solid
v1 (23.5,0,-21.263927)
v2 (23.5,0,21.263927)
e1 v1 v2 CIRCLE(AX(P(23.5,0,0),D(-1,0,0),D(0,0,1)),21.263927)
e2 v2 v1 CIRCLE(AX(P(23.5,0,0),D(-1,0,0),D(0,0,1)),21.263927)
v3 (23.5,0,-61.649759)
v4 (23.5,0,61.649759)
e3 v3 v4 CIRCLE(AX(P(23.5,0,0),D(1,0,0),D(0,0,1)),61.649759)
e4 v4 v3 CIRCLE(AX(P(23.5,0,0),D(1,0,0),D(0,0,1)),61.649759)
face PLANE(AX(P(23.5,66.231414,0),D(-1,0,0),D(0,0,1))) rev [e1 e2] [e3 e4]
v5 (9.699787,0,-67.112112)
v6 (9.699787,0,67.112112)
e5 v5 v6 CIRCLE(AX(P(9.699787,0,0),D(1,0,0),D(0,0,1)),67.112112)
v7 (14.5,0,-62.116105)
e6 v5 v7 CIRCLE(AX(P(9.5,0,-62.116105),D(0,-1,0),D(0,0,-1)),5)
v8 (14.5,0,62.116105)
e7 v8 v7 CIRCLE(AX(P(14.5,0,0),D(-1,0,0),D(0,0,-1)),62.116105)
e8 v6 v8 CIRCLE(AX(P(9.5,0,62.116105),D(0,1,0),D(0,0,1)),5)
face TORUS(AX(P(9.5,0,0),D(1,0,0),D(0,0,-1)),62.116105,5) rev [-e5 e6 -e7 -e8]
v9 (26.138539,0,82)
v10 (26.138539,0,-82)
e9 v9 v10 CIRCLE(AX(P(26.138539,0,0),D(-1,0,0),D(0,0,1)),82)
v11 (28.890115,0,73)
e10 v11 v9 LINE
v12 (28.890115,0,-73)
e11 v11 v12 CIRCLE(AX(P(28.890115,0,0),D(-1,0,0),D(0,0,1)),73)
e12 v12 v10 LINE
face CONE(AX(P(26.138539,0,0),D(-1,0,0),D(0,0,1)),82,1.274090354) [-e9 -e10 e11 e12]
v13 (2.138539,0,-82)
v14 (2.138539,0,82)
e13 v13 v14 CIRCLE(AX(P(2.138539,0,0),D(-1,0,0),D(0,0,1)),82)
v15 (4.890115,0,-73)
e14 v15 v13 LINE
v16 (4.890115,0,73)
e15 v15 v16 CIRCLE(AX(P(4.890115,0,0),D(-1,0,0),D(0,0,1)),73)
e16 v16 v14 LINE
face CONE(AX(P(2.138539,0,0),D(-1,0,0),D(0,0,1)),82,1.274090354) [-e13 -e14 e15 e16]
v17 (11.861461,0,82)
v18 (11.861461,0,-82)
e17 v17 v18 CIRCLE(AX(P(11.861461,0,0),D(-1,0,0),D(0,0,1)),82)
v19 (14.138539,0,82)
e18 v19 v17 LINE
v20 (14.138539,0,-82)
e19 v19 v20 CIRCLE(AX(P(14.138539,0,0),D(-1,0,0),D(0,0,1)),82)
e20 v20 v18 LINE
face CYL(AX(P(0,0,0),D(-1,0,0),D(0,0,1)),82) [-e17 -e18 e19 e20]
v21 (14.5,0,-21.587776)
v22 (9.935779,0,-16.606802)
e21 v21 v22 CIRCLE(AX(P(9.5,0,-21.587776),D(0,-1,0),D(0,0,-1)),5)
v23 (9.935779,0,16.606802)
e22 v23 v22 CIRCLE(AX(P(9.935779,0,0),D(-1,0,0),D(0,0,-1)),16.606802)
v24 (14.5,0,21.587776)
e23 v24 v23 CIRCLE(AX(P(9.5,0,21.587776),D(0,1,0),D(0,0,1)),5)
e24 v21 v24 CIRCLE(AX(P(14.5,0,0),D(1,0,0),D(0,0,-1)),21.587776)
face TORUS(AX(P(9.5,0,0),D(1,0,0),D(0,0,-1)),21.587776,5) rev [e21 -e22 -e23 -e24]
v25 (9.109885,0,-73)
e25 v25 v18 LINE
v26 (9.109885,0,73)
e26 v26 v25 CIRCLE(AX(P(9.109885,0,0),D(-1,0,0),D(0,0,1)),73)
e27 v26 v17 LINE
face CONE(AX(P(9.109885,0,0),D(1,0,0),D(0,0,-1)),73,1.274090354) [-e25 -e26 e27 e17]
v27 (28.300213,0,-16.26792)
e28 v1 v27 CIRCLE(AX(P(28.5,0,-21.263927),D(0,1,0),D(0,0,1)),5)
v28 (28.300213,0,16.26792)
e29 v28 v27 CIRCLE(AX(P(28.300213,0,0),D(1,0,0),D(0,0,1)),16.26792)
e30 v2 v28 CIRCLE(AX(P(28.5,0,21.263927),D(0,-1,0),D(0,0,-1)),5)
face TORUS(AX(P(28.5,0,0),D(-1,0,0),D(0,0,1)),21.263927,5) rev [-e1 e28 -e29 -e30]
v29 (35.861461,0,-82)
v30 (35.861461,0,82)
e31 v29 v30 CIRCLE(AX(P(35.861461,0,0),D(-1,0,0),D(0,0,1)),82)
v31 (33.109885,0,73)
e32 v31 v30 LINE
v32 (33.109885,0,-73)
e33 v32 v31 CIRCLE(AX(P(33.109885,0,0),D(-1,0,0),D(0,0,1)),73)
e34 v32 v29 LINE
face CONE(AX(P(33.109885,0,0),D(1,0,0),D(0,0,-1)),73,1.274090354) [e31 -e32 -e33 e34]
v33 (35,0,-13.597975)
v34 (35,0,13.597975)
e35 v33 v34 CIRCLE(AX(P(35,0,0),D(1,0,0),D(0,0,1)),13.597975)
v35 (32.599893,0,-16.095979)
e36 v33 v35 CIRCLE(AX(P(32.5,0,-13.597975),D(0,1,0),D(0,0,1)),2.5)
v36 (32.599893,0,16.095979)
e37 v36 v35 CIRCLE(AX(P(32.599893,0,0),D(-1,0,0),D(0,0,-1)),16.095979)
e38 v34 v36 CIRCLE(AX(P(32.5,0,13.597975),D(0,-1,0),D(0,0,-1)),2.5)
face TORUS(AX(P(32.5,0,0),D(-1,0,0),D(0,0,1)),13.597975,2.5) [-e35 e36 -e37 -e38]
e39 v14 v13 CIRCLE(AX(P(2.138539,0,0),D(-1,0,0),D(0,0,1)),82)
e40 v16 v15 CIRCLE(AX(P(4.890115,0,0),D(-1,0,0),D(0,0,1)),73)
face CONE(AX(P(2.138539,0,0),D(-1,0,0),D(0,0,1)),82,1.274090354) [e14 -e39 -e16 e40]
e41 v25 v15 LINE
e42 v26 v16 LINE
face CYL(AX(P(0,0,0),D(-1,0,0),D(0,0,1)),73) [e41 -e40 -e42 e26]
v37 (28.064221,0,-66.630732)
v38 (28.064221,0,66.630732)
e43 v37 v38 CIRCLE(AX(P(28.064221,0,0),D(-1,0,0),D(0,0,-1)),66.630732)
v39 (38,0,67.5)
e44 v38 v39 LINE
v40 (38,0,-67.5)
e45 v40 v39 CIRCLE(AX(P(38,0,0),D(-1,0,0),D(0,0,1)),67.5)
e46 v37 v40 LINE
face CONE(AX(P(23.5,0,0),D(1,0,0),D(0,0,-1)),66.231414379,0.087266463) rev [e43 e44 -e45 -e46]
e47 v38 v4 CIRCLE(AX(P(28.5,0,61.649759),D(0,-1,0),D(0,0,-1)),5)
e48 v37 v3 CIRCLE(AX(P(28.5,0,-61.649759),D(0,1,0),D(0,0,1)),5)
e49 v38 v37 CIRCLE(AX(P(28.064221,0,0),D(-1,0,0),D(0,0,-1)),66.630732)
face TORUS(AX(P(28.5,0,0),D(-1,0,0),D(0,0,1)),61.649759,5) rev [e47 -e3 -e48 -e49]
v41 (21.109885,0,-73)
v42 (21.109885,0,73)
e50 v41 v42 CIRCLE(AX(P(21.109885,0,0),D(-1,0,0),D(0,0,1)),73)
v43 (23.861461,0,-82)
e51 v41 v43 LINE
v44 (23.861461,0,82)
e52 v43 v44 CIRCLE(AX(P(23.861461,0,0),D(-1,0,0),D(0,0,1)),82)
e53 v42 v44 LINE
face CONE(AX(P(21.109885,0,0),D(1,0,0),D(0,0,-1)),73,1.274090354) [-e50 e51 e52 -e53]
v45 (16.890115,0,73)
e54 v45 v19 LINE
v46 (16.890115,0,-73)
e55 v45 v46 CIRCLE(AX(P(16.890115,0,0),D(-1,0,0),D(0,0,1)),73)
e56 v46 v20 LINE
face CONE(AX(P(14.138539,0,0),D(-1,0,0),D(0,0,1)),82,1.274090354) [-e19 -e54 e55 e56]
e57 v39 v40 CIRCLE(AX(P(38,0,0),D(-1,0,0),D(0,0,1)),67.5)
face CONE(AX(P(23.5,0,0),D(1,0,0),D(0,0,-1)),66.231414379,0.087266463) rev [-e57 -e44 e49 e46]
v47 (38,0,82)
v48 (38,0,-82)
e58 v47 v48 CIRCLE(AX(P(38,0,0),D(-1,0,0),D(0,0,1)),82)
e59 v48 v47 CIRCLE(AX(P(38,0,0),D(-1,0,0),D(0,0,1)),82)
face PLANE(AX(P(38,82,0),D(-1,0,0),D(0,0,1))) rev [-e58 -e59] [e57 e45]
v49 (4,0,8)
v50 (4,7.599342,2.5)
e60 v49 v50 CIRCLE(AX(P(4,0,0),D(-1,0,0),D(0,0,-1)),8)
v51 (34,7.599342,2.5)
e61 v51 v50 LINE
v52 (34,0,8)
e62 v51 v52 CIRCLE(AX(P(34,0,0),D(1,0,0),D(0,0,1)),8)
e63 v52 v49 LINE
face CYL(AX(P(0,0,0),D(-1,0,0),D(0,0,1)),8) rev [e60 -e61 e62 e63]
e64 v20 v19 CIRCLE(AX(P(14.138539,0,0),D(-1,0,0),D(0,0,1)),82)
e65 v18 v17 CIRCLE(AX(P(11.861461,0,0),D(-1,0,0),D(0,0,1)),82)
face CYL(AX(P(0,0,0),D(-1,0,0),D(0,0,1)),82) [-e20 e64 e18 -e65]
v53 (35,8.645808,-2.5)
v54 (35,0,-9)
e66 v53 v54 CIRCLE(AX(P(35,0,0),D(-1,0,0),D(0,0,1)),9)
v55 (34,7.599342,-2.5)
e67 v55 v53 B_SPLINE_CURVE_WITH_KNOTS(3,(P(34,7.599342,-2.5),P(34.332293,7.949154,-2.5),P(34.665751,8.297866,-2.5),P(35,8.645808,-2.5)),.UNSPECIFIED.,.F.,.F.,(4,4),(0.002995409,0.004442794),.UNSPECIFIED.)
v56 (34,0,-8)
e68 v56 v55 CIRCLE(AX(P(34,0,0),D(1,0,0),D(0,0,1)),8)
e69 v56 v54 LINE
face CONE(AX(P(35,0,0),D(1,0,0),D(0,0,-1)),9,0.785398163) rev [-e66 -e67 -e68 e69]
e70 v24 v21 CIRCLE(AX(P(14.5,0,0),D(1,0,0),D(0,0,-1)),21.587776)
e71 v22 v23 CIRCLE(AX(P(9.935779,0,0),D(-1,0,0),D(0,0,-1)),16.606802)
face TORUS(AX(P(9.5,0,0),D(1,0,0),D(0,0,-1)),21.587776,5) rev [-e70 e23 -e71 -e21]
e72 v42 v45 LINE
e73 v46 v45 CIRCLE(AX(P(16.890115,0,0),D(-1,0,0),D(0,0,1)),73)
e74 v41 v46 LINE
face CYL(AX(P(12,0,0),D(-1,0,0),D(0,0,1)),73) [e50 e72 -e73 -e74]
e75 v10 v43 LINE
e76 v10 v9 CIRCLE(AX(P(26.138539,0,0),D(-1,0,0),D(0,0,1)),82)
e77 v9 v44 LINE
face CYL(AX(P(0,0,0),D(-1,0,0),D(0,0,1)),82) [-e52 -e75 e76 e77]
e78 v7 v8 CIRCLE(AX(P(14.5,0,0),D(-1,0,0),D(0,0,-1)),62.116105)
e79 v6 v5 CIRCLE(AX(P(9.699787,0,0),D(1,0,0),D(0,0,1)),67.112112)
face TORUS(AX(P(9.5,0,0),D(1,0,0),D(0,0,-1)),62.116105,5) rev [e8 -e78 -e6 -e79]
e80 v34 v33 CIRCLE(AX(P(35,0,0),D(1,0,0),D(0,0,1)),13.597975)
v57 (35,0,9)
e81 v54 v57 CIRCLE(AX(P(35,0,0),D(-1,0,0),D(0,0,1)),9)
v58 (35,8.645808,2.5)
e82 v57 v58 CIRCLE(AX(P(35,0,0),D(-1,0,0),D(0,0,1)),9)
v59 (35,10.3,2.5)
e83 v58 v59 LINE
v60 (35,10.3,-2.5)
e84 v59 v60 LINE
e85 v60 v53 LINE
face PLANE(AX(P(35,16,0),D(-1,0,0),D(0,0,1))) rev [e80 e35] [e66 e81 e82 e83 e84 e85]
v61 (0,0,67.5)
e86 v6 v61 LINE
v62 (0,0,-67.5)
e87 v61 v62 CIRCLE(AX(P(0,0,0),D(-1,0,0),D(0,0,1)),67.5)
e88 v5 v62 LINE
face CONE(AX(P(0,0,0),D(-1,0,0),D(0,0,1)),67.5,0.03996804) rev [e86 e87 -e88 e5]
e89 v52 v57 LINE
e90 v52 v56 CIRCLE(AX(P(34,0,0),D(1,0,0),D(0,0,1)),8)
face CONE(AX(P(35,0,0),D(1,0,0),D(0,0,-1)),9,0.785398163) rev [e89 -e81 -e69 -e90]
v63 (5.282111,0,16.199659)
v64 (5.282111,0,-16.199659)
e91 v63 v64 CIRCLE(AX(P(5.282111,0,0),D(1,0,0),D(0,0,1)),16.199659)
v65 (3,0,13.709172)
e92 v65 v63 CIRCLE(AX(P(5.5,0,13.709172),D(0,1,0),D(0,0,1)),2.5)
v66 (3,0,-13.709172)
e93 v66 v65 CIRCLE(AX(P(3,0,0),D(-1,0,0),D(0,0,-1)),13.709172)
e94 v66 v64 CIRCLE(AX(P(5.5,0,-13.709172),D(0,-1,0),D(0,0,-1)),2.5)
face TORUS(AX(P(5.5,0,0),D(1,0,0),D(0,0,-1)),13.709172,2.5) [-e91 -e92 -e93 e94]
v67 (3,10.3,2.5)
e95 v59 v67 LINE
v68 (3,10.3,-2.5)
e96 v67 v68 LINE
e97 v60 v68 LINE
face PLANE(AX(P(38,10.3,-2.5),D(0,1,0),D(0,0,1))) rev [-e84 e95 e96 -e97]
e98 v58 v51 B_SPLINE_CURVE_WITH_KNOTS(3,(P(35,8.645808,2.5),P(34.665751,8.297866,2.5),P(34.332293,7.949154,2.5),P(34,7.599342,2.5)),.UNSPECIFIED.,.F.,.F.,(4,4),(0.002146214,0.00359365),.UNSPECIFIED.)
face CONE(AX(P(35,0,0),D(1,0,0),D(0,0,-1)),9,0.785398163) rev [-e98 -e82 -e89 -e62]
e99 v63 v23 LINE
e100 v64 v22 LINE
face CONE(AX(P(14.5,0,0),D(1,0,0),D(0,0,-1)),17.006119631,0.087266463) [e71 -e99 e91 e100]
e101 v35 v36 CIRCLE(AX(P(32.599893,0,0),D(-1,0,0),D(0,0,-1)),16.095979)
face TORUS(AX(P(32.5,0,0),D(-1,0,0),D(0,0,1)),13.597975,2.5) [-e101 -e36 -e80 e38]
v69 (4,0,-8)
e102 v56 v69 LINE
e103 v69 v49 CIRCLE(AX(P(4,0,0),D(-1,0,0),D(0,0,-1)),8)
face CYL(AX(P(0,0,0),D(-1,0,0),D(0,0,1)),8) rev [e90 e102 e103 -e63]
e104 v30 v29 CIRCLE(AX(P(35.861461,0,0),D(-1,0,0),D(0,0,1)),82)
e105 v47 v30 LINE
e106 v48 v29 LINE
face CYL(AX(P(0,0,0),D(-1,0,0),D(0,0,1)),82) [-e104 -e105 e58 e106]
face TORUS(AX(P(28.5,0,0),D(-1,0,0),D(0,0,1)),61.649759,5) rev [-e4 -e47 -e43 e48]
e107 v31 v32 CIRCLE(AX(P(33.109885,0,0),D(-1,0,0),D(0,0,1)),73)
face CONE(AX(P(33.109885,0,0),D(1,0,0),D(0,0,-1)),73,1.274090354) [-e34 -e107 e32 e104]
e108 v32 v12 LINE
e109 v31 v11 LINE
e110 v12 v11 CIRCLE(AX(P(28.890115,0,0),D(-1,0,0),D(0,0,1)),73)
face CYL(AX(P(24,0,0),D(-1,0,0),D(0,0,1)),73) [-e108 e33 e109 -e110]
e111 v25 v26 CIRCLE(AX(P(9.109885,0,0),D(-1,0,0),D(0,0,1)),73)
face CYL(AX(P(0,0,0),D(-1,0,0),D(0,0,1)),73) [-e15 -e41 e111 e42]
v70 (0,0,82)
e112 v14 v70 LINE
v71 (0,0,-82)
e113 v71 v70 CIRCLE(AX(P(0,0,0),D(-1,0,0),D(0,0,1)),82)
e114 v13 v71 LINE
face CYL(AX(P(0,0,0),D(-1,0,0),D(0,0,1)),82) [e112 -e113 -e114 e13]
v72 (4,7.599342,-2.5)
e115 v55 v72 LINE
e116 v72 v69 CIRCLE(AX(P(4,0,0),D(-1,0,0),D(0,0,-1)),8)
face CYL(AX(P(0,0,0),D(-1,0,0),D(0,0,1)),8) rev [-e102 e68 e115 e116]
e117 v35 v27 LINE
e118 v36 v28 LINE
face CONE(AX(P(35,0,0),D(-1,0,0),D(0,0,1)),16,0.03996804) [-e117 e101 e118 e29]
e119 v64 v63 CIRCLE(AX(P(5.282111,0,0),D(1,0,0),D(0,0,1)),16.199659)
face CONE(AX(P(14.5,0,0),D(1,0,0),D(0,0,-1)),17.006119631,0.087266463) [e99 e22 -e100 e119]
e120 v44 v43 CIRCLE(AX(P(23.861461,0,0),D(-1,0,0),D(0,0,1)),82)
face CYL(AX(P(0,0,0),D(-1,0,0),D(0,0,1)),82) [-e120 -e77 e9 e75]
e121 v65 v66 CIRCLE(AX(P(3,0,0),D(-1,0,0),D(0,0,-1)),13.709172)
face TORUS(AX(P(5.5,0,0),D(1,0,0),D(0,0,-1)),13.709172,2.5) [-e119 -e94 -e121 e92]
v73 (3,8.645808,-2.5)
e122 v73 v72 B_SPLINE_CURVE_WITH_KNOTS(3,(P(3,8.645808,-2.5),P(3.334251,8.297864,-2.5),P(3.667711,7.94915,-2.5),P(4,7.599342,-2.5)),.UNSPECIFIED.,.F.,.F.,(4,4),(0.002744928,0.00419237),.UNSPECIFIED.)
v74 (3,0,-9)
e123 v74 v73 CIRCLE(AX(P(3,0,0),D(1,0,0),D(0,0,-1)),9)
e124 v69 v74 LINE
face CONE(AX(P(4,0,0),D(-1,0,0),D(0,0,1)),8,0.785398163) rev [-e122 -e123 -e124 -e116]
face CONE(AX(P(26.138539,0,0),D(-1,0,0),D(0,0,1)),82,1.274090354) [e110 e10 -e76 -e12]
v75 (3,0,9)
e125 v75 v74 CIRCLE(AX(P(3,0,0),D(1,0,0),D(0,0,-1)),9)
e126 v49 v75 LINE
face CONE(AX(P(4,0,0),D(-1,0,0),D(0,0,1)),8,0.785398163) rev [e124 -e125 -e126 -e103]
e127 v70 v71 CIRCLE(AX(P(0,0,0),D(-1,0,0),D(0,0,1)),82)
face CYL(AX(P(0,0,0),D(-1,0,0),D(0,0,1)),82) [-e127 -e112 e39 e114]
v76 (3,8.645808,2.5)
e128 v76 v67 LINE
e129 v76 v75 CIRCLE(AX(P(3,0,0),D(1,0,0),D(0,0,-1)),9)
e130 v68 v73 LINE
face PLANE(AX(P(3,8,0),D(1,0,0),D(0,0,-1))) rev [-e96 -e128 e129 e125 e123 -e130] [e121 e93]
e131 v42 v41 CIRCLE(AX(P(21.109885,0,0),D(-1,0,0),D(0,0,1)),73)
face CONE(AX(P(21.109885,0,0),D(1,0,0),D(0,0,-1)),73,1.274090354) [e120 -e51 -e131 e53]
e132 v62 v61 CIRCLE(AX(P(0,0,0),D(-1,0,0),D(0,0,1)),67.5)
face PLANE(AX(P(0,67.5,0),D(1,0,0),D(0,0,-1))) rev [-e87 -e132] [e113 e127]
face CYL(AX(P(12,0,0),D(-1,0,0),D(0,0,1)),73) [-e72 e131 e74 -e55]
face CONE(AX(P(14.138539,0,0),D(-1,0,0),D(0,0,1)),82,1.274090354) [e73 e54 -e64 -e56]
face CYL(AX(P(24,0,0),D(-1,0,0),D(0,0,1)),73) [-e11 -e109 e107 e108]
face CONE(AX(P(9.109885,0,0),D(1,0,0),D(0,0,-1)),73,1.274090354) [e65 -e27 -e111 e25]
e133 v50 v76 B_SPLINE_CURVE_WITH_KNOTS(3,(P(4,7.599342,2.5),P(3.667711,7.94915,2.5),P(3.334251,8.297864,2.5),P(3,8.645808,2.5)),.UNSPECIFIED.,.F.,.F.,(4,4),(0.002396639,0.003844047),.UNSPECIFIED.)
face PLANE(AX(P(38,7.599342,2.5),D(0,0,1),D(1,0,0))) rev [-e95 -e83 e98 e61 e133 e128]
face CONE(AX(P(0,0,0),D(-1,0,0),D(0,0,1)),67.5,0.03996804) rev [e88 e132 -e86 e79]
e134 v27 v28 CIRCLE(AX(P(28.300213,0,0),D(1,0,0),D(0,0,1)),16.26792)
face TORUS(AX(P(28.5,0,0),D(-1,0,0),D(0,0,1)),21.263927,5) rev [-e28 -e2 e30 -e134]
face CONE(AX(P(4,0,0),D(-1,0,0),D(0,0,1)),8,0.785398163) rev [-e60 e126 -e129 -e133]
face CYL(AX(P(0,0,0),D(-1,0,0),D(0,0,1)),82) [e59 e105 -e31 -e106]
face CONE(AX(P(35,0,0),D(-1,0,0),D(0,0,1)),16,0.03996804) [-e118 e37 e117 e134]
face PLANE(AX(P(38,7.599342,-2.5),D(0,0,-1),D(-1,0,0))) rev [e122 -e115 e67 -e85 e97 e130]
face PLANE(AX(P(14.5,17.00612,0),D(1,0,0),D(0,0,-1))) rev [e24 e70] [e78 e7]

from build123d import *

# Parameters (mm, degrees)
PATTERN_LINEAR_940_COUNT = 3
PATTERN_LINEAR_940_PITCH = 12
CHAMFER_1_SIZE           = 1
SKETCH_4_W               = 5
SKETCH_4_H               = 2.700657875
CUT_EXTRUDE_1_DEPTH      = 122.132159231
FILLET_1_R               = 5
FILLET_2_R               = 2.5


with BuildPart() as part:
    # 草图1 → 旋转1 (revolve)
    with BuildSketch(Plane.XY, mode=Mode.PRIVATE) as revolve_1_sk:
        Polygon((3, 8), (3, 16), (14.5, 17.006119631), (14.5, 66.920154632), (0, 67.5), (0, 82), (38, 82), (38, 67.5), (23.5, 66.231414379), (23.5, 16.459877361), (35, 16), (35, 8), align=None)
    revolve(revolve_1_sk.sketch.rotate(Axis((0, 0, 0), (1, 0, 0)), 90), axis=Axis((0, 0, 0), (1, 0, 0)))

    # 草图2 → 切除-旋转1 (revolve, cut)
    with BuildSketch(Plane.XY, mode=Mode.PRIVATE) as cut_revolve_1_sk:
        Polygon((9.10988523, 73), (11.861461363, 82), (2.138538637, 82), (4.89011477, 73), align=None)
    cut_revolve_1 = revolve(cut_revolve_1_sk.sketch.rotate(Axis((0, 0, 0), (1, 0, 0)), 90), axis=Axis((0, 0, 0), (1, 0, 0)), mode=Mode.SUBTRACT)

    # Pattern Linear 940: 切除-旋转1 ×3
    with Locations(*[(i * PATTERN_LINEAR_940_PITCH, 0, 0) for i in range(1, PATTERN_LINEAR_940_COUNT)]):
        add(cut_revolve_1, mode=Mode.SUBTRACT)

    # 倒角1
    chamfer_1_edges = [part.edges().sort_by_distance(p)[0] for p in [
        (3, 0, -8),
        (35, 0, -8),
    ]]
    chamfer(chamfer_1_edges, length=CHAMFER_1_SIZE)

    # 草图4 → 切除-拉伸1 (cut, through all)
    with BuildSketch(Plane.ZY.offset(-3)):
        with Locations((0, 8.949671014)):
            Rectangle(SKETCH_4_W, SKETCH_4_H)
    extrude(amount=-CUT_EXTRUDE_1_DEPTH, mode=Mode.SUBTRACT)

    # 圆角1
    fillet_1_edges = [part.edges().sort_by_distance(p)[0] for p in [
        (14.5, 0, -66.920154632),
        (14.5, 0, -17.006119631),
        (23.5, 0, -16.459877361),
        (23.5, 0, -66.231414379),
    ]]
    fillet(fillet_1_edges, radius=FILLET_1_R)

    # 圆角2
    fillet_2_edges = [part.edges().sort_by_distance(p)[0] for p in [
        (3, 0, -16),
        (35, 0, -16),
    ]]
    fillet(fillet_2_edges, radius=FILLET_2_R)


solid = part.part
